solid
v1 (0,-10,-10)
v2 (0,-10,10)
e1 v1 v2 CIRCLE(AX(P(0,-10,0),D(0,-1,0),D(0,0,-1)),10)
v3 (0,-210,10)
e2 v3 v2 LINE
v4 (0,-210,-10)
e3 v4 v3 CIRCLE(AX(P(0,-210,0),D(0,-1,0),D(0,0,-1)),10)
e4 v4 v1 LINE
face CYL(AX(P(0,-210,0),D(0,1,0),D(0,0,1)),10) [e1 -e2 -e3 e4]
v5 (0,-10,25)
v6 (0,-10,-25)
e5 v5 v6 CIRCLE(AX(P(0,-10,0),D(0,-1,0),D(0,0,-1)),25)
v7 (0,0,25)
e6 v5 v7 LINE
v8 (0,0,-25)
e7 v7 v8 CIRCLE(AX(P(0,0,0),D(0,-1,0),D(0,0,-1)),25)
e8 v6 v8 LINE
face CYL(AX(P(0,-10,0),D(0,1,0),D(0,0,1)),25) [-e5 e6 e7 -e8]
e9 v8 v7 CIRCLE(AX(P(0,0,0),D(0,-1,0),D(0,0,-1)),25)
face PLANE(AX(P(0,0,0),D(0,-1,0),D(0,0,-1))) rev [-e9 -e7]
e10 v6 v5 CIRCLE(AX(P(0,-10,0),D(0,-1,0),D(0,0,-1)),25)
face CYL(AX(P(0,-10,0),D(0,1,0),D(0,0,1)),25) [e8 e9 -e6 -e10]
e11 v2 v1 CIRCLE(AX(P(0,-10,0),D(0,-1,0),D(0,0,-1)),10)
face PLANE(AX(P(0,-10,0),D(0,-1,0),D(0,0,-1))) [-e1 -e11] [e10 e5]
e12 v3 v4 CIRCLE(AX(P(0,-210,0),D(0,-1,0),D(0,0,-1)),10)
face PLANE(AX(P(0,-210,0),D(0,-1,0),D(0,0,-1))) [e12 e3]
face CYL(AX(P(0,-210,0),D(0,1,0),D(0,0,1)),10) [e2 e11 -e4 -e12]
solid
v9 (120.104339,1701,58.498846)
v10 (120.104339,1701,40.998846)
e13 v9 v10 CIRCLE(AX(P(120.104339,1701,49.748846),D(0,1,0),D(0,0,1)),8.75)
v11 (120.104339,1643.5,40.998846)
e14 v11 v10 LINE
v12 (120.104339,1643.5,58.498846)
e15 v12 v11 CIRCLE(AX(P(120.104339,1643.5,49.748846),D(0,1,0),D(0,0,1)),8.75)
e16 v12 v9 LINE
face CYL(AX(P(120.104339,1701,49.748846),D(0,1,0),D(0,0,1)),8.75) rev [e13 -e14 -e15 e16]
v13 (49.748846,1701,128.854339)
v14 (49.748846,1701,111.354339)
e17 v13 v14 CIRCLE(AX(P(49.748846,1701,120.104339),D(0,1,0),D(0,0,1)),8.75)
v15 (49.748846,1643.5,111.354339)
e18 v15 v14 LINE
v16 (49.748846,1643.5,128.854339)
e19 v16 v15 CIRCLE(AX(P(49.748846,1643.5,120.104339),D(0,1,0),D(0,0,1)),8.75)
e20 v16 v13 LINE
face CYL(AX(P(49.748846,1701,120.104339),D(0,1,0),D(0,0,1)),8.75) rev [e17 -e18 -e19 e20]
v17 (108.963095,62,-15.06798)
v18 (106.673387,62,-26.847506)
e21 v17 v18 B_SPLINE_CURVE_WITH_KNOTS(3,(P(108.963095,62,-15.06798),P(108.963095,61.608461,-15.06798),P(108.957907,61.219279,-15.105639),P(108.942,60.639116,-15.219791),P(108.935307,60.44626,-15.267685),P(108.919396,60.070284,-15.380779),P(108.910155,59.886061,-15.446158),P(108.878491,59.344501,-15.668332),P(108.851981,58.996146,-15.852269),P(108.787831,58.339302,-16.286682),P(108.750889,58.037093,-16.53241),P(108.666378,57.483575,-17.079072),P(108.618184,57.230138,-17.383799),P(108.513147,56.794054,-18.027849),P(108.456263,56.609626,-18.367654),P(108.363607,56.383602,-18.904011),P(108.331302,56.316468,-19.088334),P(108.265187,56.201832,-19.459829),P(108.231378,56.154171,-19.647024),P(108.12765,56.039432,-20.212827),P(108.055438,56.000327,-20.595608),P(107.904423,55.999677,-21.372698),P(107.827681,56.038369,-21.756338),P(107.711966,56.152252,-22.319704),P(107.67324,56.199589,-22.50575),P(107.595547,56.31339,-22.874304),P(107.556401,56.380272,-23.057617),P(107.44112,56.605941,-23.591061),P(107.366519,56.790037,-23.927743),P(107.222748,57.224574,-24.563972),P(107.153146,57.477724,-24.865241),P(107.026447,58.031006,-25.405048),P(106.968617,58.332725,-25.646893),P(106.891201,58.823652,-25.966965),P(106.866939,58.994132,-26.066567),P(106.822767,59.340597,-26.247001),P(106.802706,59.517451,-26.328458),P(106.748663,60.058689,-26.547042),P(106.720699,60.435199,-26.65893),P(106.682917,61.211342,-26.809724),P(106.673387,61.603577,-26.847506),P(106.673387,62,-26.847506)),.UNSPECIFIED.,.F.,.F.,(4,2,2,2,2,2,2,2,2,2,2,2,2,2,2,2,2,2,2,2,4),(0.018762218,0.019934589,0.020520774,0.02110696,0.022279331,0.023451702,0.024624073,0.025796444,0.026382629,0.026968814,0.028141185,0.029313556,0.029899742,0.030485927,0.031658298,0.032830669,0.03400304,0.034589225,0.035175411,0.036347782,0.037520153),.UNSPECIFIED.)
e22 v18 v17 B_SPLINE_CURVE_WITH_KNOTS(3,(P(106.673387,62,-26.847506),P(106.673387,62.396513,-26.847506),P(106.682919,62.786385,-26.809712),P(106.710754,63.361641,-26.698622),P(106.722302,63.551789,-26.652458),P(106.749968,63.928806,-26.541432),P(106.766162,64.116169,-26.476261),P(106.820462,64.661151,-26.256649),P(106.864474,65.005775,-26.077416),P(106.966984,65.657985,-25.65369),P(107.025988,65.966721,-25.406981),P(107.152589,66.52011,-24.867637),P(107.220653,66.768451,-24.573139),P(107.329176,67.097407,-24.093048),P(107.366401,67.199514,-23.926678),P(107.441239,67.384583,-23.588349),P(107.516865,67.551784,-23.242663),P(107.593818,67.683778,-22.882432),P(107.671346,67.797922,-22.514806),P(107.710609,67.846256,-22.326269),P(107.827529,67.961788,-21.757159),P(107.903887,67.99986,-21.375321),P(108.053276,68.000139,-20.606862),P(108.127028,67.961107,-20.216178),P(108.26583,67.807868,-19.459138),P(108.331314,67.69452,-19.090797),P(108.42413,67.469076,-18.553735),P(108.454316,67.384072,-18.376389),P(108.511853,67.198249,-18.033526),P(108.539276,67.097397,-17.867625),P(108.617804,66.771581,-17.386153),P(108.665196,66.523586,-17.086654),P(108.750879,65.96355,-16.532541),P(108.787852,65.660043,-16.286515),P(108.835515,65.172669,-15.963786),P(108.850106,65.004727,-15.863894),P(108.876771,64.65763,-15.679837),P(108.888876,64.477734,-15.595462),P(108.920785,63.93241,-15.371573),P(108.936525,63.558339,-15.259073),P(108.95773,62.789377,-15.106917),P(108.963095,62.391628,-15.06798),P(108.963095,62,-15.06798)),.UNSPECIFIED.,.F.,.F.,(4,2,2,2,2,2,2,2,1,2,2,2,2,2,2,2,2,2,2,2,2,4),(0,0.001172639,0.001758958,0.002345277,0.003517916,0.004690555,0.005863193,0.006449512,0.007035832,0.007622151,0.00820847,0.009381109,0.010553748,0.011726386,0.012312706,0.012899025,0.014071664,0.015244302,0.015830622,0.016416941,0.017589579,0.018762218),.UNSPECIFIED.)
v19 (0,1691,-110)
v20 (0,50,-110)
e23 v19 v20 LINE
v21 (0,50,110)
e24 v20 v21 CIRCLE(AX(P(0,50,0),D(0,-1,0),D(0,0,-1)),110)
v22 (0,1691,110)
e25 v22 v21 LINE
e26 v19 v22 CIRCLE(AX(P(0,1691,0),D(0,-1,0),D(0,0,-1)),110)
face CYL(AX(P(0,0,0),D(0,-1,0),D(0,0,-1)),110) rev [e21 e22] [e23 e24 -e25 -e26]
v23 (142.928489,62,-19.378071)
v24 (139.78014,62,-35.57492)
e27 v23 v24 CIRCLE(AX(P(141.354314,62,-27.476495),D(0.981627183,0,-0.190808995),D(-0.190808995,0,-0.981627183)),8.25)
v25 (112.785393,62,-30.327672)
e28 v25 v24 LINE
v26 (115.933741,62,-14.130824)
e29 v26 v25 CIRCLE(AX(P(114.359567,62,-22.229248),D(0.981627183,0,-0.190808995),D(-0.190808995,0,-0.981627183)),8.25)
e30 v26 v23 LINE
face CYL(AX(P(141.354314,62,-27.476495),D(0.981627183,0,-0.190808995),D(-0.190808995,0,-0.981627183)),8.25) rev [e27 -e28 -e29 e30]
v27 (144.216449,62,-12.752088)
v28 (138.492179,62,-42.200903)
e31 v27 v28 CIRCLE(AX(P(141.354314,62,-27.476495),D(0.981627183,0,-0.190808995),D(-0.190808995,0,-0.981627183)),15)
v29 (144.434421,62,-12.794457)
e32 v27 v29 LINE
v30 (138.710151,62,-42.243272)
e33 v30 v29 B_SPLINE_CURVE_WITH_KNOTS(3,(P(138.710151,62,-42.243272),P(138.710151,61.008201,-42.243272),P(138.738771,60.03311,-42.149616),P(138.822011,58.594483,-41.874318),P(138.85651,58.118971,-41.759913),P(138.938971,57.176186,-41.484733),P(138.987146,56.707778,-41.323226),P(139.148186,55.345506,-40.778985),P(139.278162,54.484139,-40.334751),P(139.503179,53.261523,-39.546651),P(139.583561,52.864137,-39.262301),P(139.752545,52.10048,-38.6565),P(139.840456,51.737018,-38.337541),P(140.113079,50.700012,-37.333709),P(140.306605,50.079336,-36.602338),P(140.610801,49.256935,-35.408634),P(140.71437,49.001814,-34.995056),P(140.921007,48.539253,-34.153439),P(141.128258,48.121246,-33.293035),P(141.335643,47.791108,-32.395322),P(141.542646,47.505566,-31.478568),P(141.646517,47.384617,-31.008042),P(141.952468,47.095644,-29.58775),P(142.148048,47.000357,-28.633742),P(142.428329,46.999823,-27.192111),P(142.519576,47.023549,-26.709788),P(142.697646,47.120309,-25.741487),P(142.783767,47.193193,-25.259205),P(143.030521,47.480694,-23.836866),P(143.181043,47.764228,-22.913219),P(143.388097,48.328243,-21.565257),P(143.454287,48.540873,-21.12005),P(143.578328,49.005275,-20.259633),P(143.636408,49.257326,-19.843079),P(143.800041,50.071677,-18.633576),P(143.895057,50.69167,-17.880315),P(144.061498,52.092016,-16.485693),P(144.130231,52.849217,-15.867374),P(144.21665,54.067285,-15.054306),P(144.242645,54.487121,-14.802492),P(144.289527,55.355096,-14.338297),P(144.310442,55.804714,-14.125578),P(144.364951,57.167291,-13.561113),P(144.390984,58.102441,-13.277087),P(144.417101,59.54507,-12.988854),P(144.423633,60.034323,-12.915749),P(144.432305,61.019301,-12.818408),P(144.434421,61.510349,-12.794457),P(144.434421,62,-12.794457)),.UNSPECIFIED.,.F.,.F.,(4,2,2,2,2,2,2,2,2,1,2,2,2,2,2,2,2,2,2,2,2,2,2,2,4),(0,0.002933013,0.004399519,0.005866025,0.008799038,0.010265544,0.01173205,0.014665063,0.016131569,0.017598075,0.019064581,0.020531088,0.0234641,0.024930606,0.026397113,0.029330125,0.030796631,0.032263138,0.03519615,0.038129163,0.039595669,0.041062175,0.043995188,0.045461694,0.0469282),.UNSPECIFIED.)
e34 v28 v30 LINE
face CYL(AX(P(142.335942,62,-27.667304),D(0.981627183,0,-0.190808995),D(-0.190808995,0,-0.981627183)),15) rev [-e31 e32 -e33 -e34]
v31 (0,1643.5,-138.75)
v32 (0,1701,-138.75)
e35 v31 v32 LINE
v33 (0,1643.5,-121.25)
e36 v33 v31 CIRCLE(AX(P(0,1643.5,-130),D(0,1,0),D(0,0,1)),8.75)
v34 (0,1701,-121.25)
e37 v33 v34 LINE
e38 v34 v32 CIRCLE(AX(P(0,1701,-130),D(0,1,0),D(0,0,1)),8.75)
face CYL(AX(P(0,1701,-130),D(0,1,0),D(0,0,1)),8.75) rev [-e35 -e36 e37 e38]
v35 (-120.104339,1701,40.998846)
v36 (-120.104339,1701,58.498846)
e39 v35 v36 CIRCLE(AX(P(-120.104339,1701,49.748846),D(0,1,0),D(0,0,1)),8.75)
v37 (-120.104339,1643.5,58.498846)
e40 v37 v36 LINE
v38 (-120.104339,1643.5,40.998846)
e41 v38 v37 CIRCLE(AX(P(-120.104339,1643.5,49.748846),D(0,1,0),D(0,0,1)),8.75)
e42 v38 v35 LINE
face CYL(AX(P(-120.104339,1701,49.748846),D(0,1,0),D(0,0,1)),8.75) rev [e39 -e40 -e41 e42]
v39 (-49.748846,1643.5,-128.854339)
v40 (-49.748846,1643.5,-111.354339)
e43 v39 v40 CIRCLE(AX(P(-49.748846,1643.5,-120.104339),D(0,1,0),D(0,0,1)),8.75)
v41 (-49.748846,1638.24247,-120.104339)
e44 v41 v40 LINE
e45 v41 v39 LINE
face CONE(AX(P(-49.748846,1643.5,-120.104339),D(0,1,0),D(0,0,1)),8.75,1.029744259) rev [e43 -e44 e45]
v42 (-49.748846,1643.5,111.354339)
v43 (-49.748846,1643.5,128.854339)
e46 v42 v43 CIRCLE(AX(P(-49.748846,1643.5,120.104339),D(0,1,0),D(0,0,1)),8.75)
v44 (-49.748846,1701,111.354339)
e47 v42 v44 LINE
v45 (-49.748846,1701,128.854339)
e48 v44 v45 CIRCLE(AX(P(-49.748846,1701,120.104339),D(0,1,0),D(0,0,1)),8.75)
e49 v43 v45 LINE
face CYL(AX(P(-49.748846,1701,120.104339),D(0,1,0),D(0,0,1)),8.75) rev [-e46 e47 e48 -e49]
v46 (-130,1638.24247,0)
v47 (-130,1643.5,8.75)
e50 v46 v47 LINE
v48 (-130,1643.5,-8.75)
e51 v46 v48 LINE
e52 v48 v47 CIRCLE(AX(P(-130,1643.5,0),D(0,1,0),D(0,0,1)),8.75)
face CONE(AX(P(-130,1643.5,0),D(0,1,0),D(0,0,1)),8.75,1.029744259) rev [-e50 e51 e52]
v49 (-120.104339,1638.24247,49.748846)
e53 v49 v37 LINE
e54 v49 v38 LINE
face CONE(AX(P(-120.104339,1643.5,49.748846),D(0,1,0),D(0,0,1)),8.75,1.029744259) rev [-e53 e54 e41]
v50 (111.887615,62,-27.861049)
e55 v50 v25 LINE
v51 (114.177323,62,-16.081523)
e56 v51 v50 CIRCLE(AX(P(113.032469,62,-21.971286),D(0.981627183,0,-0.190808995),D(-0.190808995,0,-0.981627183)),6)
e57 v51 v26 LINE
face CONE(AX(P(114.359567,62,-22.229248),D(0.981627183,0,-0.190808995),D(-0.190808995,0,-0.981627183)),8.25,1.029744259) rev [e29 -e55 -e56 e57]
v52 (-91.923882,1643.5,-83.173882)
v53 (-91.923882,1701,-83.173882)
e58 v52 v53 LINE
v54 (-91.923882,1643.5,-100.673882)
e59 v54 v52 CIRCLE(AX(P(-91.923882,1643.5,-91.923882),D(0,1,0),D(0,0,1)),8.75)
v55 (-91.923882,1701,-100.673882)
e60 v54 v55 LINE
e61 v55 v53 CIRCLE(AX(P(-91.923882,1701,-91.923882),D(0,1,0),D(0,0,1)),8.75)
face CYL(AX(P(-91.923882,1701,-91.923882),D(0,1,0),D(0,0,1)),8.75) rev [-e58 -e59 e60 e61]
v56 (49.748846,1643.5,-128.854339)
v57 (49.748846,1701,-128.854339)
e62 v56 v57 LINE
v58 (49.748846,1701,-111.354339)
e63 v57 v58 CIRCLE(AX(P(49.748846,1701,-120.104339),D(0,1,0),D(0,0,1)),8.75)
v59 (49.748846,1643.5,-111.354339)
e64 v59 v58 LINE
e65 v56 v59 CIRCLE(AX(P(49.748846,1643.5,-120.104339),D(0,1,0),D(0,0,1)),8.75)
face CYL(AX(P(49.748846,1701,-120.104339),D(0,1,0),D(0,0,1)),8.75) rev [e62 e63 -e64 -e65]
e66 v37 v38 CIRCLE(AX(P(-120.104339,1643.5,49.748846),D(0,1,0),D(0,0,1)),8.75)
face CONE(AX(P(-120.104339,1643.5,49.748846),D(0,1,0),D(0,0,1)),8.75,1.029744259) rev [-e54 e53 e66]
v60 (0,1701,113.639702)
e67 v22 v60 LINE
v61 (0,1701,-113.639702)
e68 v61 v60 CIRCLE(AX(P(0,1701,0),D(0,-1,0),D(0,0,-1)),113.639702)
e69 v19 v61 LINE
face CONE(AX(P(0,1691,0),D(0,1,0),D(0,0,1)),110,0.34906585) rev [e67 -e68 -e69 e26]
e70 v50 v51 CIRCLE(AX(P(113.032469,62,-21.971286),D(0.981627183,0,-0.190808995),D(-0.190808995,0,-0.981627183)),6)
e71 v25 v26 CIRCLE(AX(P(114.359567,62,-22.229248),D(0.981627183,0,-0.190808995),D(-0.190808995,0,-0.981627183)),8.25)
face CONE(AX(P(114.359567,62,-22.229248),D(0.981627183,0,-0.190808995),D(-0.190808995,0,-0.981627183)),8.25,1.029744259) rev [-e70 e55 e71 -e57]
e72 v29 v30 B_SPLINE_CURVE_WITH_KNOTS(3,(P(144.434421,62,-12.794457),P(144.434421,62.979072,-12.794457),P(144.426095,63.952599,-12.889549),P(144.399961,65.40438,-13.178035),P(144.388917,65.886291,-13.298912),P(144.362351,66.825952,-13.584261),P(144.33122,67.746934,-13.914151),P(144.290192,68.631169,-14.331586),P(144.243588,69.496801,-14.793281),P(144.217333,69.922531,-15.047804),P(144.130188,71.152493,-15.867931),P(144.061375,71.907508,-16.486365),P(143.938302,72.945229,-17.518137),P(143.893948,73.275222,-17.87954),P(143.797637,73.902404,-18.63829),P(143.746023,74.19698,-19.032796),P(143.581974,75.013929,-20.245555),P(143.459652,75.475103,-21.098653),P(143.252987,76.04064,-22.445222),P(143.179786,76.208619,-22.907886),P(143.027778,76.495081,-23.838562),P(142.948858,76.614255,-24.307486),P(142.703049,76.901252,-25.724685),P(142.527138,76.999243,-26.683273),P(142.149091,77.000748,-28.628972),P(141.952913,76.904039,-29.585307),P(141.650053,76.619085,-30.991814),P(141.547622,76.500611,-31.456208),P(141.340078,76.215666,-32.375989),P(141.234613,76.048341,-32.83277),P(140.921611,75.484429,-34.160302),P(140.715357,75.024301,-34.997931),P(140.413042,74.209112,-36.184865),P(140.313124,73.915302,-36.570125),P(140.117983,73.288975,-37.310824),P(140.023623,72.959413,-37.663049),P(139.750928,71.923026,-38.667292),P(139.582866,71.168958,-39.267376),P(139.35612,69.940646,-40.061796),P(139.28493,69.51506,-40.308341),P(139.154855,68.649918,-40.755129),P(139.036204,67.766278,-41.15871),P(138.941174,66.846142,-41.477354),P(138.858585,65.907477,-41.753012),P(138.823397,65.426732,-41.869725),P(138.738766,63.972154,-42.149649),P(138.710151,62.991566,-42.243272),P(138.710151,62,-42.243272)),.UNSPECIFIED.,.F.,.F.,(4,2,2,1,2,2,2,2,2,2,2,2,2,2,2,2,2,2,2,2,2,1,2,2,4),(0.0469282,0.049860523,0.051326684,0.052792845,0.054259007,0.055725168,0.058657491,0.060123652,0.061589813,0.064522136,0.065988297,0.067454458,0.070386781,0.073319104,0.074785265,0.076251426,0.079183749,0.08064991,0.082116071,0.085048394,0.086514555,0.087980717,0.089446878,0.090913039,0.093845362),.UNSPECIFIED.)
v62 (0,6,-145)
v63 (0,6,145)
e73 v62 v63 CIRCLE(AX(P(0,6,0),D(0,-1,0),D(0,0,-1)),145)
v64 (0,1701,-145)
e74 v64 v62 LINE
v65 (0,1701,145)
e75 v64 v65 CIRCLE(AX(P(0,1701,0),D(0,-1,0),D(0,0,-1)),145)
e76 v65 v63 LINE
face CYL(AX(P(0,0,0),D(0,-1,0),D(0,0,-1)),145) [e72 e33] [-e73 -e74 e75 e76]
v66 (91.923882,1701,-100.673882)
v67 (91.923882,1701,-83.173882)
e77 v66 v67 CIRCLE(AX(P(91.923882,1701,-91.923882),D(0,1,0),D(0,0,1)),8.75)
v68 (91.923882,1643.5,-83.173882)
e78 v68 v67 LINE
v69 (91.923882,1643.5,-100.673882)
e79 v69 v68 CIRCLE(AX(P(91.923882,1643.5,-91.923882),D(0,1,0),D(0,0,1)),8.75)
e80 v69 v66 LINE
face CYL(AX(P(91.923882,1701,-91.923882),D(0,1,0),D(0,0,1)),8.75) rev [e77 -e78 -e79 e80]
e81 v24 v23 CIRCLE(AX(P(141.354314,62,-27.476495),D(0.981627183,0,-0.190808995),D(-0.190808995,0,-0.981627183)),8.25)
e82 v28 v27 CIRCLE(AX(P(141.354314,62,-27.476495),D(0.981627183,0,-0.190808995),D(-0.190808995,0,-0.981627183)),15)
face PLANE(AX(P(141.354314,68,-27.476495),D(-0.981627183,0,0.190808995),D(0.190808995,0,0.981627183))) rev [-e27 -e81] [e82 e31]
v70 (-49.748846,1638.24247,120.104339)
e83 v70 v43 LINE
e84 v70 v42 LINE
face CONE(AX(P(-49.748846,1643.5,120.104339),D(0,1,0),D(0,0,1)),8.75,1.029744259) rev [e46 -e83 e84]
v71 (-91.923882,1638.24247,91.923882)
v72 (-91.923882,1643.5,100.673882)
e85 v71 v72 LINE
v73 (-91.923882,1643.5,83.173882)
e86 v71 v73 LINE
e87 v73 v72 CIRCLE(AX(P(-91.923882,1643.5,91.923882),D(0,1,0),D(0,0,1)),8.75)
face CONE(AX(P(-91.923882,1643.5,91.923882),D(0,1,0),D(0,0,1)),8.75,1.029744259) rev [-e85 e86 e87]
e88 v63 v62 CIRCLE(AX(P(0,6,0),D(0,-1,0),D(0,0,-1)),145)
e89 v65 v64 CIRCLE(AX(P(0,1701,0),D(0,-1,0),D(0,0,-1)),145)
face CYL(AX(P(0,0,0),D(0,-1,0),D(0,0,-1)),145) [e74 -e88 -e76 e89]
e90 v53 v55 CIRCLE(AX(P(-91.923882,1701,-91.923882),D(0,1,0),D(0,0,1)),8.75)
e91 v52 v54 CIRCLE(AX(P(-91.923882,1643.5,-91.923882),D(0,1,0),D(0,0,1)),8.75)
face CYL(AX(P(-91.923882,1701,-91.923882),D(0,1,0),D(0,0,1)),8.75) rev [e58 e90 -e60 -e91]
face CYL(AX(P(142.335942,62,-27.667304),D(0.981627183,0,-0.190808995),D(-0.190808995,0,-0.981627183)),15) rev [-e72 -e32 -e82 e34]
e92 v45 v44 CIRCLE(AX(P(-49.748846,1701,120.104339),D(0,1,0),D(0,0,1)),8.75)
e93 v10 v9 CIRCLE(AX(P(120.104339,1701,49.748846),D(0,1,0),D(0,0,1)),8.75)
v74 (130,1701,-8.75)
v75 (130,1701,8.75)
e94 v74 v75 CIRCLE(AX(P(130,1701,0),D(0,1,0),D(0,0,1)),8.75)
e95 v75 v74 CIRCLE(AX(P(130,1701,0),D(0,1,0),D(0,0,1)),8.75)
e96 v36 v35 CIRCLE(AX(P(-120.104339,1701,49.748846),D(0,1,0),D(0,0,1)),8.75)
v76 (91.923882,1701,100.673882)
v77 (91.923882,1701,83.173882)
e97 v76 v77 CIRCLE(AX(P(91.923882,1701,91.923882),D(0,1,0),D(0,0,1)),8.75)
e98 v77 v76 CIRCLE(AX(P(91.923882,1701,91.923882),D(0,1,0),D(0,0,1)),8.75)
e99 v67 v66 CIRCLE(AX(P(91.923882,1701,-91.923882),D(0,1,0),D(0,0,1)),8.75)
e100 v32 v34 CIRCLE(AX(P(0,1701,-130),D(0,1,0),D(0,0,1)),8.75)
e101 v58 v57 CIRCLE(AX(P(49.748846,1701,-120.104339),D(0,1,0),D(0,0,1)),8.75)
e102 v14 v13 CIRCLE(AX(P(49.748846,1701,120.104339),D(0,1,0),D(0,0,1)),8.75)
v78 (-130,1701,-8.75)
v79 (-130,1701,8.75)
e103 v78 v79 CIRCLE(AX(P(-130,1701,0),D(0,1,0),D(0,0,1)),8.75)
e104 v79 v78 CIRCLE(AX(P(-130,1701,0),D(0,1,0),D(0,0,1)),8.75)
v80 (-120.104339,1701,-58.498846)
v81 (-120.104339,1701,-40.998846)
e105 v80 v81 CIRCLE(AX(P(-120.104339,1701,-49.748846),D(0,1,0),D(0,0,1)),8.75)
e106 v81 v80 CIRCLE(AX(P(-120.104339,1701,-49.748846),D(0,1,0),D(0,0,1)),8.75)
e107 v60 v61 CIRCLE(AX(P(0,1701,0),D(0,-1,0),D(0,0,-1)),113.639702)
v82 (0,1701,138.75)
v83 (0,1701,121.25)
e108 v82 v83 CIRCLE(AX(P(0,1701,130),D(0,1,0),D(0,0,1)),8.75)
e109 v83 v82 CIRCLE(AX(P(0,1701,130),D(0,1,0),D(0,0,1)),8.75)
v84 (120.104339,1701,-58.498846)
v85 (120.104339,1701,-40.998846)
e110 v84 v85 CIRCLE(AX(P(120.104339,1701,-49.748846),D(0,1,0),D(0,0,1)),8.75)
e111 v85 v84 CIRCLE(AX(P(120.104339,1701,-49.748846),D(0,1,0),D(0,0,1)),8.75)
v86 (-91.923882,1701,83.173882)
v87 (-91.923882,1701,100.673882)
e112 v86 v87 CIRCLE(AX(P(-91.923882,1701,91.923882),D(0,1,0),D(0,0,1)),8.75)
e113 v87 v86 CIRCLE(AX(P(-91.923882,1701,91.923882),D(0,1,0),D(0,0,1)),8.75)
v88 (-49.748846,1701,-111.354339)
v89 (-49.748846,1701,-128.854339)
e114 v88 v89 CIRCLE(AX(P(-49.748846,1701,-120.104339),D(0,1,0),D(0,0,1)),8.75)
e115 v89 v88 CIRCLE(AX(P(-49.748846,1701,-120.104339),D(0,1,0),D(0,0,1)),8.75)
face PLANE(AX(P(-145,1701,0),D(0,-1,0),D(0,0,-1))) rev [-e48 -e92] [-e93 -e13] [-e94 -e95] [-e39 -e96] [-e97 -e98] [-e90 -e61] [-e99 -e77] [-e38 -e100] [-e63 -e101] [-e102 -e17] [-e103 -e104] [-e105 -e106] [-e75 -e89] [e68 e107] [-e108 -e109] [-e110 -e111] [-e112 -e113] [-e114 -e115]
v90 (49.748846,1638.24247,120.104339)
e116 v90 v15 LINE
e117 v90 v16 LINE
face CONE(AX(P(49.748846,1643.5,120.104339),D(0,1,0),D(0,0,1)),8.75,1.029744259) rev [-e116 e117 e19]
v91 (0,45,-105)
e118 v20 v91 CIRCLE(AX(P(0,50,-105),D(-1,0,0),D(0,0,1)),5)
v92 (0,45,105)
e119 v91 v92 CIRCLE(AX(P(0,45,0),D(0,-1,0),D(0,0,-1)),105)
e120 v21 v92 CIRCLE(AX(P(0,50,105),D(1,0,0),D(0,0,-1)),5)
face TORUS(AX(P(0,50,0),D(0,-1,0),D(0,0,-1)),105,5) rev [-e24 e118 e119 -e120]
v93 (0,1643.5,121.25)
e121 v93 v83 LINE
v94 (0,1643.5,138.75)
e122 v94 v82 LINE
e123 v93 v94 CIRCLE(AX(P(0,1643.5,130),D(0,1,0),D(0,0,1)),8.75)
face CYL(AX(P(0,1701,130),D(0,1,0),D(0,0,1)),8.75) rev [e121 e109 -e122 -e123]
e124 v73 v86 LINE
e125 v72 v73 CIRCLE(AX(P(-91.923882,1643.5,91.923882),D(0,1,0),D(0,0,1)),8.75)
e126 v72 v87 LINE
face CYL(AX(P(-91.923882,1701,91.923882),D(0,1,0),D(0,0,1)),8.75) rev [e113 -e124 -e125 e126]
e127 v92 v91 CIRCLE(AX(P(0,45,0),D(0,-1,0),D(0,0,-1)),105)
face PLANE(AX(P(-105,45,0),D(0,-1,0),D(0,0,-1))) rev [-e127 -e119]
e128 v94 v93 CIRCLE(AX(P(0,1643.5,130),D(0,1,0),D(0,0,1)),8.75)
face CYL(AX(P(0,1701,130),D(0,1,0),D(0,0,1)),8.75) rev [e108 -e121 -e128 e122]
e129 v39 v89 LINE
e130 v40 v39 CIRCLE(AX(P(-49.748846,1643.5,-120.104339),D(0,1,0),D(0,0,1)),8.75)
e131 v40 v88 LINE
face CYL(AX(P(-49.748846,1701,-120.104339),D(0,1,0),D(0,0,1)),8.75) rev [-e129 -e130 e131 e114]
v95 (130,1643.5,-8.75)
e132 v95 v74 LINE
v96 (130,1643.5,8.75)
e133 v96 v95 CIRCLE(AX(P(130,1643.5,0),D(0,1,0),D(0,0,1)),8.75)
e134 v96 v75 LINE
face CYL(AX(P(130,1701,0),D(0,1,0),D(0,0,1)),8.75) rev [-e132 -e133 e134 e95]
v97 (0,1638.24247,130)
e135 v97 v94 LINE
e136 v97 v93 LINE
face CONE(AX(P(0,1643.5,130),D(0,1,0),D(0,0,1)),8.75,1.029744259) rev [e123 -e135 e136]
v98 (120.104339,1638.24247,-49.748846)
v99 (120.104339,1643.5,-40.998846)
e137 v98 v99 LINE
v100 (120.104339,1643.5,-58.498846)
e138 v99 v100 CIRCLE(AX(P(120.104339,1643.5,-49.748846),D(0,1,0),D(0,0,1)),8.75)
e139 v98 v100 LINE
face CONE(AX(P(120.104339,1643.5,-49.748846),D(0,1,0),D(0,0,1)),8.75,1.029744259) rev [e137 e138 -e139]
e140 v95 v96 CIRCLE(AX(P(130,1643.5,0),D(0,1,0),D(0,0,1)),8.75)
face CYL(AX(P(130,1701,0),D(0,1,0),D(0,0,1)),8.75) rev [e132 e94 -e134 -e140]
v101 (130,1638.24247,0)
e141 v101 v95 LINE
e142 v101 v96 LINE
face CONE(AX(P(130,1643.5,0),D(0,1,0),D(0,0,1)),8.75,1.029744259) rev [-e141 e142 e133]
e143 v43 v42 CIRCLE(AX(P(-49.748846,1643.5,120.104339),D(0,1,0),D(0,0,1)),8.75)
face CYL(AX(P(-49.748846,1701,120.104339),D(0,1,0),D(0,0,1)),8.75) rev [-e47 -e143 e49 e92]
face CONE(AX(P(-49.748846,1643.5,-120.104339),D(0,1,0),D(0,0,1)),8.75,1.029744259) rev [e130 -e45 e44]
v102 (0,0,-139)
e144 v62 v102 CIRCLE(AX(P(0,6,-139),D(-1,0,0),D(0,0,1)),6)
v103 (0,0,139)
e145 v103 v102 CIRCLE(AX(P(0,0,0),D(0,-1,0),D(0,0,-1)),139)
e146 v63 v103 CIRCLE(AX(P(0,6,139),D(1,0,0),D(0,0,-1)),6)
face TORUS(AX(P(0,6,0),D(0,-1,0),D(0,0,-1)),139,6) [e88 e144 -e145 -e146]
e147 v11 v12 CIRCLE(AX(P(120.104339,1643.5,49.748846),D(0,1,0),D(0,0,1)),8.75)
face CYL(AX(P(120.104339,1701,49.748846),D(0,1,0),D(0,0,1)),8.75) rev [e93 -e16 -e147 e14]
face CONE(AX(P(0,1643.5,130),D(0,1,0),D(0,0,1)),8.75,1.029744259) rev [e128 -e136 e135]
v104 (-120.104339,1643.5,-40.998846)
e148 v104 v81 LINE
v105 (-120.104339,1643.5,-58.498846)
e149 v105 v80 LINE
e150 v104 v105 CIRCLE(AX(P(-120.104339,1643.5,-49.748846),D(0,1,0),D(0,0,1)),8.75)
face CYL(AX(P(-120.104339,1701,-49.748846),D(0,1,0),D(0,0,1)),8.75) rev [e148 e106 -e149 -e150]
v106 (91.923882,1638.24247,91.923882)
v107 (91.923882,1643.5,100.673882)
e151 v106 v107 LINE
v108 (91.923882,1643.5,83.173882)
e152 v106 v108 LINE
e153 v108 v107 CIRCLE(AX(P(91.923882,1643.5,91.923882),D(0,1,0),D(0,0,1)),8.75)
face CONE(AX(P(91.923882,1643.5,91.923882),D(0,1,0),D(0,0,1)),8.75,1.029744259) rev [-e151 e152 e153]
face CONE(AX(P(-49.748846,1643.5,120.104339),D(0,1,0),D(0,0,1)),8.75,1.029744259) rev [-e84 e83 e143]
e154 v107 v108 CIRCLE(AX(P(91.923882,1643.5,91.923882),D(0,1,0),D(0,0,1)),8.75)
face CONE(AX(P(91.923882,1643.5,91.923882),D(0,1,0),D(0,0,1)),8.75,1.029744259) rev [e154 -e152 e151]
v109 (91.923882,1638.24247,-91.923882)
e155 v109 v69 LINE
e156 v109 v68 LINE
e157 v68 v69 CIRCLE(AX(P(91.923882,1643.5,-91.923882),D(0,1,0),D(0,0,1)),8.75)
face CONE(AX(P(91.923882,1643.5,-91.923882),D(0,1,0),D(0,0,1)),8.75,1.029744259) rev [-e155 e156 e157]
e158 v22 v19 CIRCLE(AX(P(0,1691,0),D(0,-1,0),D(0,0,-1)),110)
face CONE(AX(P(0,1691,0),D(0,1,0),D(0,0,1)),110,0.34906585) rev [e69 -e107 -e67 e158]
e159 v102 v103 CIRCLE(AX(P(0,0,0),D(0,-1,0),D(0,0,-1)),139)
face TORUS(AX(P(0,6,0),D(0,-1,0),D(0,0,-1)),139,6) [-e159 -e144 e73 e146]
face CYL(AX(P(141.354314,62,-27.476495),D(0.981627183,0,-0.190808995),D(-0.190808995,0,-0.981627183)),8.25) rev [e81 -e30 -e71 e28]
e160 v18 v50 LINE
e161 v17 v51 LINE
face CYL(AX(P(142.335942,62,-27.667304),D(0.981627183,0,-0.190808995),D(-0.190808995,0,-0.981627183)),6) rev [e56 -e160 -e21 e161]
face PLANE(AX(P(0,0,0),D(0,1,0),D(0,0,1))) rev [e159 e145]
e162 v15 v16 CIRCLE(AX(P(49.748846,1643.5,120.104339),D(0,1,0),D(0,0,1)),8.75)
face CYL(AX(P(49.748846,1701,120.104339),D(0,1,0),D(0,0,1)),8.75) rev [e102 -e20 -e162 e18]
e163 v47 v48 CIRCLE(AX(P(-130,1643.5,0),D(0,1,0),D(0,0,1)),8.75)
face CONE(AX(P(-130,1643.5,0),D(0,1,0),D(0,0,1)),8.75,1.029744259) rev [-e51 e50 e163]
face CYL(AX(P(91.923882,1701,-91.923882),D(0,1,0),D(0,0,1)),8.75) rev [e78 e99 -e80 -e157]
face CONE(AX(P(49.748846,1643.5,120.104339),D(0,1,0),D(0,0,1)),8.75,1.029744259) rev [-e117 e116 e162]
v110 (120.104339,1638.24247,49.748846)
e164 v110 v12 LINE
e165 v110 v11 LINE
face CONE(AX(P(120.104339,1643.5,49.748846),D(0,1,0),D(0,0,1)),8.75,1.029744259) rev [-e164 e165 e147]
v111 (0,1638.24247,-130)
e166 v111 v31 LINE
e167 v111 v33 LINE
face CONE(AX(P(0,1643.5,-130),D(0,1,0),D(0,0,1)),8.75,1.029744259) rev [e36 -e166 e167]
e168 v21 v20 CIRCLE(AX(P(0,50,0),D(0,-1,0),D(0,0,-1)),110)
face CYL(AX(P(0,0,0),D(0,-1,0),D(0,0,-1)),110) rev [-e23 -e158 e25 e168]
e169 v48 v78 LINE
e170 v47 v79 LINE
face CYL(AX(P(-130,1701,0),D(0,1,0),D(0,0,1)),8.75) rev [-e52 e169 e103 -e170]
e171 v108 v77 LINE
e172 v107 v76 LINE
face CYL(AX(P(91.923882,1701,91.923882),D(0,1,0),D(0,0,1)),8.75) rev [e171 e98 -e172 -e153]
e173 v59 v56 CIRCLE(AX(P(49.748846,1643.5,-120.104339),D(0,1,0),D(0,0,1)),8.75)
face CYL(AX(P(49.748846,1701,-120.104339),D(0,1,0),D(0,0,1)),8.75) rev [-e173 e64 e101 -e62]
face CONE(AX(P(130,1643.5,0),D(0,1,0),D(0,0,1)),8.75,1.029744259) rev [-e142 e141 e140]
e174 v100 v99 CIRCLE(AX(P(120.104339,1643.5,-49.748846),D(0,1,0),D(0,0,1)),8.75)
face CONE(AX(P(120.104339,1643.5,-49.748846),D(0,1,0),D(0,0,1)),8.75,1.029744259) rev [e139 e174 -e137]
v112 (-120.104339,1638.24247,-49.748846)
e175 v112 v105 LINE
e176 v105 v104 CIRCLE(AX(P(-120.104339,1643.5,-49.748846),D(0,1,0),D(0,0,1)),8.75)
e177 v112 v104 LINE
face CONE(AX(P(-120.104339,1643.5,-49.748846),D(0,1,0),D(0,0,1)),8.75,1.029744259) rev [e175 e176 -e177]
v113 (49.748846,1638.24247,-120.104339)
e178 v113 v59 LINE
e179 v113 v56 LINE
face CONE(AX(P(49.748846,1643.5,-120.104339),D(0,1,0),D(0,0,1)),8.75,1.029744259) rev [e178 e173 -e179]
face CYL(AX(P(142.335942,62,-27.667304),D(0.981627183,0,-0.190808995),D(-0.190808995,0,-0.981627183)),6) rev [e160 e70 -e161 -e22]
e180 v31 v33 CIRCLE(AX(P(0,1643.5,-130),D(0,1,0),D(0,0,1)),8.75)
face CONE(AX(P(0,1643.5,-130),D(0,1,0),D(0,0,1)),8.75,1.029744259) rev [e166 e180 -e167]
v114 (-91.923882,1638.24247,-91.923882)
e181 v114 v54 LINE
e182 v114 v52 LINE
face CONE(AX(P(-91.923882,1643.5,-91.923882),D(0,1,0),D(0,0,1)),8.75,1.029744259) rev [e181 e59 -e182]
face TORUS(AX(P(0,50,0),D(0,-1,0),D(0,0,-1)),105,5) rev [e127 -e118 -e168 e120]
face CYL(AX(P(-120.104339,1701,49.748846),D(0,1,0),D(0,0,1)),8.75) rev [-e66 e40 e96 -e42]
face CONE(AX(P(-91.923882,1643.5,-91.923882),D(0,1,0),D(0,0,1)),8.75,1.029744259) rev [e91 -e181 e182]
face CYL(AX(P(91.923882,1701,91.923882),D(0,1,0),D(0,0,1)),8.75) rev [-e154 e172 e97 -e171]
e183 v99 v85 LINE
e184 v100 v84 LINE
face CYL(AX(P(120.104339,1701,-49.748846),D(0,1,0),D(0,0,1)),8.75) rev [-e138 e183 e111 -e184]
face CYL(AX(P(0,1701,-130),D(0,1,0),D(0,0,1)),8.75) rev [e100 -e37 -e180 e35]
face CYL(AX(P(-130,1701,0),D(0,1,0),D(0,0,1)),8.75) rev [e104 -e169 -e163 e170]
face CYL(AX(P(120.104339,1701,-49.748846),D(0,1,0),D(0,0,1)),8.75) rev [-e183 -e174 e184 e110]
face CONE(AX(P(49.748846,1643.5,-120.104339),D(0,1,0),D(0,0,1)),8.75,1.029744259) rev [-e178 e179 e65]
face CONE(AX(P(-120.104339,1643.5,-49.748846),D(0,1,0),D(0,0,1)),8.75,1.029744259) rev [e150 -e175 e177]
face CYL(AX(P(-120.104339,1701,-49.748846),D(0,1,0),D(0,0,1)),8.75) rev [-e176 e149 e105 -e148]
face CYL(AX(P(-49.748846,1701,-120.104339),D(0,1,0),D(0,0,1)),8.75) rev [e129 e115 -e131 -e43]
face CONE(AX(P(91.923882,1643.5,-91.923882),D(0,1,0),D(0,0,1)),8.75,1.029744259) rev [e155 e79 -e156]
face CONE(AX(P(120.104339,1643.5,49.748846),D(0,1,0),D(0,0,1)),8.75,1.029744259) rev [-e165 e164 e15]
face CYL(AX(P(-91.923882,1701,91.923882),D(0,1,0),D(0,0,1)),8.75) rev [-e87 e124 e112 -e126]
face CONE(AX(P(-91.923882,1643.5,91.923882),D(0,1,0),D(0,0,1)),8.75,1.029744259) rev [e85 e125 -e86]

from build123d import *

# Parameters (mm, degrees)
M20_TAPPED_HOLE1_D                                   = 17.5
M20_TAPPED_HOLE1_DEPTH                               = 57.5
M20_TAPPED_HOLE1_TIP                                 = 5.257530416
HOLE_SIZE_PER_SOCKET_HEAD_CAP_SCREW_TYPE_D           = 12
HOLE_SIZE_PER_SOCKET_HEAD_CAP_SCREW_TYPE_DEPTH       = 50
HOLE_SIZE_PER_SOCKET_HEAD_CAP_SCREW_TYPE_CBORE_D     = 30
HOLE_SIZE_PER_SOCKET_HEAD_CAP_SCREW_TYPE_CBORE_DEPTH = 1
HOLE_SIZE_PER_SOCKET_HEAD_CAP_SCREW_TYPE_TIP         = 3.605163714
M18X1_5_TAPPED_HOLE1_D                               = 16.5
M18X1_5_TAPPED_HOLE1_DEPTH                           = 27.5
M18X1_5_TAPPED_HOLE1_TIP                             = 4.957100107
SKETCH7_R                                            = 25
BOSS_EXTRUDE1_DEPTH                                  = 10
SKETCH8_R                                            = 10
BOSS_EXTRUDE2_DEPTH                                  = 200


with BuildPart() as part:
    # Sketch1 → Revolve1 (revolve)
    with BuildSketch(Plane.XY, mode=Mode.PRIVATE) as revolve1_sk:
        with BuildLine():
            Line((0, 0), (-139, 0))
            ThreePointArc((-139, 0), (-143.242640687, 1.757359313), (-145, 6))
            Line((-145, 6), (-145, 1701))
            Line((-145, 1701), (-113.639702343, 1701))
            Line((-113.639702343, 1701), (-110, 1691))
            Line((-110, 1691), (-110, 50))
            ThreePointArc((-110, 50), (-108.535533906, 46.464466094), (-105, 45))
            Line((-105, 45), (0, 45))
            Line((0, 45), (0, 0))
        make_face()
    revolve(revolve1_sk.sketch.rotate(Axis((0, 0, 0), (0, 1, 0)), 270), axis=Axis((0, 0, 0), (0, 1, 0)))

    # M20 Tapped Hole1
    with Locations(Plane(origin=(0, 1701, 0), x_dir=(1, 0, 0), z_dir=(0, 1, 0))):
        with Locations((-130, 0), (-120.104339226, 49.748846207), (-91.923881554, 91.923881554), (-49.748846207, 120.104339226), (0, 130), (49.748846207, 120.104339226), (91.923881554, 91.923881554), (120.104339226, 49.748846207), (130, 0), (120.104339226, -49.748846207), (91.923881554, -91.923881554), (49.748846207, -120.104339226), (0, -130), (-49.748846207, -120.104339226), (-91.923881554, -91.923881554), (-120.104339226, -49.748846207)):
            Hole(M20_TAPPED_HOLE1_D / 2, depth=M20_TAPPED_HOLE1_DEPTH)
            with Locations((0, 0, -(M20_TAPPED_HOLE1_DEPTH + M20_TAPPED_HOLE1_TIP / 2))):  # 118° drill point
                Cone(0, M20_TAPPED_HOLE1_D / 2, M20_TAPPED_HOLE1_TIP, mode=Mode.SUBTRACT)

    # Hole size per socket head cap screw type1
    with Locations(Plane(origin=(142.3359416, 62, -27.66730433), x_dir=(0.190808995377, 0, 0.981627183448), z_dir=(0.981627183448, 0, -0.190808995377))):
        with Locations((0, 0)):
            CounterBoreHole(HOLE_SIZE_PER_SOCKET_HEAD_CAP_SCREW_TYPE_D / 2, HOLE_SIZE_PER_SOCKET_HEAD_CAP_SCREW_TYPE_CBORE_D / 2, HOLE_SIZE_PER_SOCKET_HEAD_CAP_SCREW_TYPE_CBORE_DEPTH, depth=HOLE_SIZE_PER_SOCKET_HEAD_CAP_SCREW_TYPE_DEPTH)
            with Locations((0, 0, -(HOLE_SIZE_PER_SOCKET_HEAD_CAP_SCREW_TYPE_DEPTH + HOLE_SIZE_PER_SOCKET_HEAD_CAP_SCREW_TYPE_TIP / 2))):  # 118° drill point
                Cone(0, HOLE_SIZE_PER_SOCKET_HEAD_CAP_SCREW_TYPE_D / 2, HOLE_SIZE_PER_SOCKET_HEAD_CAP_SCREW_TYPE_TIP, mode=Mode.SUBTRACT)

    # M18x1.5 Tapped Hole1
    with Locations(Plane(origin=(141.354314416, 0, -27.476495334), x_dir=(-0.1908089953765457, 0, -0.9816271834476639), z_dir=(0.9816271834476639, 0, -0.1908089953765457))):
        with Locations((0, 62)):
            Hole(M18X1_5_TAPPED_HOLE1_D / 2, depth=M18X1_5_TAPPED_HOLE1_DEPTH)
            with Locations((0, 0, -(M18X1_5_TAPPED_HOLE1_DEPTH + M18X1_5_TAPPED_HOLE1_TIP / 2))):  # 118° drill point
                Cone(0, M18X1_5_TAPPED_HOLE1_D / 2, M18X1_5_TAPPED_HOLE1_TIP, mode=Mode.SUBTRACT)


with BuildPart() as body_2:
    # Sketch7 → Boss-Extrude1 (new body)
    with BuildSketch(Plane.XZ):
        with Locations(Location((0, 0, 0), (0, 0, 270))):
            Circle(SKETCH7_R)
    extrude(amount=BOSS_EXTRUDE1_DEPTH)

    # Sketch8 → Boss-Extrude2 (add)
    with BuildSketch(Plane.XZ.offset(10)):
        with Locations(Location((0, 0, 0), (0, 0, 270))):
            Circle(SKETCH8_R)
    extrude(amount=BOSS_EXTRUDE2_DEPTH)


solid = Compound([part.part, body_2.part])
